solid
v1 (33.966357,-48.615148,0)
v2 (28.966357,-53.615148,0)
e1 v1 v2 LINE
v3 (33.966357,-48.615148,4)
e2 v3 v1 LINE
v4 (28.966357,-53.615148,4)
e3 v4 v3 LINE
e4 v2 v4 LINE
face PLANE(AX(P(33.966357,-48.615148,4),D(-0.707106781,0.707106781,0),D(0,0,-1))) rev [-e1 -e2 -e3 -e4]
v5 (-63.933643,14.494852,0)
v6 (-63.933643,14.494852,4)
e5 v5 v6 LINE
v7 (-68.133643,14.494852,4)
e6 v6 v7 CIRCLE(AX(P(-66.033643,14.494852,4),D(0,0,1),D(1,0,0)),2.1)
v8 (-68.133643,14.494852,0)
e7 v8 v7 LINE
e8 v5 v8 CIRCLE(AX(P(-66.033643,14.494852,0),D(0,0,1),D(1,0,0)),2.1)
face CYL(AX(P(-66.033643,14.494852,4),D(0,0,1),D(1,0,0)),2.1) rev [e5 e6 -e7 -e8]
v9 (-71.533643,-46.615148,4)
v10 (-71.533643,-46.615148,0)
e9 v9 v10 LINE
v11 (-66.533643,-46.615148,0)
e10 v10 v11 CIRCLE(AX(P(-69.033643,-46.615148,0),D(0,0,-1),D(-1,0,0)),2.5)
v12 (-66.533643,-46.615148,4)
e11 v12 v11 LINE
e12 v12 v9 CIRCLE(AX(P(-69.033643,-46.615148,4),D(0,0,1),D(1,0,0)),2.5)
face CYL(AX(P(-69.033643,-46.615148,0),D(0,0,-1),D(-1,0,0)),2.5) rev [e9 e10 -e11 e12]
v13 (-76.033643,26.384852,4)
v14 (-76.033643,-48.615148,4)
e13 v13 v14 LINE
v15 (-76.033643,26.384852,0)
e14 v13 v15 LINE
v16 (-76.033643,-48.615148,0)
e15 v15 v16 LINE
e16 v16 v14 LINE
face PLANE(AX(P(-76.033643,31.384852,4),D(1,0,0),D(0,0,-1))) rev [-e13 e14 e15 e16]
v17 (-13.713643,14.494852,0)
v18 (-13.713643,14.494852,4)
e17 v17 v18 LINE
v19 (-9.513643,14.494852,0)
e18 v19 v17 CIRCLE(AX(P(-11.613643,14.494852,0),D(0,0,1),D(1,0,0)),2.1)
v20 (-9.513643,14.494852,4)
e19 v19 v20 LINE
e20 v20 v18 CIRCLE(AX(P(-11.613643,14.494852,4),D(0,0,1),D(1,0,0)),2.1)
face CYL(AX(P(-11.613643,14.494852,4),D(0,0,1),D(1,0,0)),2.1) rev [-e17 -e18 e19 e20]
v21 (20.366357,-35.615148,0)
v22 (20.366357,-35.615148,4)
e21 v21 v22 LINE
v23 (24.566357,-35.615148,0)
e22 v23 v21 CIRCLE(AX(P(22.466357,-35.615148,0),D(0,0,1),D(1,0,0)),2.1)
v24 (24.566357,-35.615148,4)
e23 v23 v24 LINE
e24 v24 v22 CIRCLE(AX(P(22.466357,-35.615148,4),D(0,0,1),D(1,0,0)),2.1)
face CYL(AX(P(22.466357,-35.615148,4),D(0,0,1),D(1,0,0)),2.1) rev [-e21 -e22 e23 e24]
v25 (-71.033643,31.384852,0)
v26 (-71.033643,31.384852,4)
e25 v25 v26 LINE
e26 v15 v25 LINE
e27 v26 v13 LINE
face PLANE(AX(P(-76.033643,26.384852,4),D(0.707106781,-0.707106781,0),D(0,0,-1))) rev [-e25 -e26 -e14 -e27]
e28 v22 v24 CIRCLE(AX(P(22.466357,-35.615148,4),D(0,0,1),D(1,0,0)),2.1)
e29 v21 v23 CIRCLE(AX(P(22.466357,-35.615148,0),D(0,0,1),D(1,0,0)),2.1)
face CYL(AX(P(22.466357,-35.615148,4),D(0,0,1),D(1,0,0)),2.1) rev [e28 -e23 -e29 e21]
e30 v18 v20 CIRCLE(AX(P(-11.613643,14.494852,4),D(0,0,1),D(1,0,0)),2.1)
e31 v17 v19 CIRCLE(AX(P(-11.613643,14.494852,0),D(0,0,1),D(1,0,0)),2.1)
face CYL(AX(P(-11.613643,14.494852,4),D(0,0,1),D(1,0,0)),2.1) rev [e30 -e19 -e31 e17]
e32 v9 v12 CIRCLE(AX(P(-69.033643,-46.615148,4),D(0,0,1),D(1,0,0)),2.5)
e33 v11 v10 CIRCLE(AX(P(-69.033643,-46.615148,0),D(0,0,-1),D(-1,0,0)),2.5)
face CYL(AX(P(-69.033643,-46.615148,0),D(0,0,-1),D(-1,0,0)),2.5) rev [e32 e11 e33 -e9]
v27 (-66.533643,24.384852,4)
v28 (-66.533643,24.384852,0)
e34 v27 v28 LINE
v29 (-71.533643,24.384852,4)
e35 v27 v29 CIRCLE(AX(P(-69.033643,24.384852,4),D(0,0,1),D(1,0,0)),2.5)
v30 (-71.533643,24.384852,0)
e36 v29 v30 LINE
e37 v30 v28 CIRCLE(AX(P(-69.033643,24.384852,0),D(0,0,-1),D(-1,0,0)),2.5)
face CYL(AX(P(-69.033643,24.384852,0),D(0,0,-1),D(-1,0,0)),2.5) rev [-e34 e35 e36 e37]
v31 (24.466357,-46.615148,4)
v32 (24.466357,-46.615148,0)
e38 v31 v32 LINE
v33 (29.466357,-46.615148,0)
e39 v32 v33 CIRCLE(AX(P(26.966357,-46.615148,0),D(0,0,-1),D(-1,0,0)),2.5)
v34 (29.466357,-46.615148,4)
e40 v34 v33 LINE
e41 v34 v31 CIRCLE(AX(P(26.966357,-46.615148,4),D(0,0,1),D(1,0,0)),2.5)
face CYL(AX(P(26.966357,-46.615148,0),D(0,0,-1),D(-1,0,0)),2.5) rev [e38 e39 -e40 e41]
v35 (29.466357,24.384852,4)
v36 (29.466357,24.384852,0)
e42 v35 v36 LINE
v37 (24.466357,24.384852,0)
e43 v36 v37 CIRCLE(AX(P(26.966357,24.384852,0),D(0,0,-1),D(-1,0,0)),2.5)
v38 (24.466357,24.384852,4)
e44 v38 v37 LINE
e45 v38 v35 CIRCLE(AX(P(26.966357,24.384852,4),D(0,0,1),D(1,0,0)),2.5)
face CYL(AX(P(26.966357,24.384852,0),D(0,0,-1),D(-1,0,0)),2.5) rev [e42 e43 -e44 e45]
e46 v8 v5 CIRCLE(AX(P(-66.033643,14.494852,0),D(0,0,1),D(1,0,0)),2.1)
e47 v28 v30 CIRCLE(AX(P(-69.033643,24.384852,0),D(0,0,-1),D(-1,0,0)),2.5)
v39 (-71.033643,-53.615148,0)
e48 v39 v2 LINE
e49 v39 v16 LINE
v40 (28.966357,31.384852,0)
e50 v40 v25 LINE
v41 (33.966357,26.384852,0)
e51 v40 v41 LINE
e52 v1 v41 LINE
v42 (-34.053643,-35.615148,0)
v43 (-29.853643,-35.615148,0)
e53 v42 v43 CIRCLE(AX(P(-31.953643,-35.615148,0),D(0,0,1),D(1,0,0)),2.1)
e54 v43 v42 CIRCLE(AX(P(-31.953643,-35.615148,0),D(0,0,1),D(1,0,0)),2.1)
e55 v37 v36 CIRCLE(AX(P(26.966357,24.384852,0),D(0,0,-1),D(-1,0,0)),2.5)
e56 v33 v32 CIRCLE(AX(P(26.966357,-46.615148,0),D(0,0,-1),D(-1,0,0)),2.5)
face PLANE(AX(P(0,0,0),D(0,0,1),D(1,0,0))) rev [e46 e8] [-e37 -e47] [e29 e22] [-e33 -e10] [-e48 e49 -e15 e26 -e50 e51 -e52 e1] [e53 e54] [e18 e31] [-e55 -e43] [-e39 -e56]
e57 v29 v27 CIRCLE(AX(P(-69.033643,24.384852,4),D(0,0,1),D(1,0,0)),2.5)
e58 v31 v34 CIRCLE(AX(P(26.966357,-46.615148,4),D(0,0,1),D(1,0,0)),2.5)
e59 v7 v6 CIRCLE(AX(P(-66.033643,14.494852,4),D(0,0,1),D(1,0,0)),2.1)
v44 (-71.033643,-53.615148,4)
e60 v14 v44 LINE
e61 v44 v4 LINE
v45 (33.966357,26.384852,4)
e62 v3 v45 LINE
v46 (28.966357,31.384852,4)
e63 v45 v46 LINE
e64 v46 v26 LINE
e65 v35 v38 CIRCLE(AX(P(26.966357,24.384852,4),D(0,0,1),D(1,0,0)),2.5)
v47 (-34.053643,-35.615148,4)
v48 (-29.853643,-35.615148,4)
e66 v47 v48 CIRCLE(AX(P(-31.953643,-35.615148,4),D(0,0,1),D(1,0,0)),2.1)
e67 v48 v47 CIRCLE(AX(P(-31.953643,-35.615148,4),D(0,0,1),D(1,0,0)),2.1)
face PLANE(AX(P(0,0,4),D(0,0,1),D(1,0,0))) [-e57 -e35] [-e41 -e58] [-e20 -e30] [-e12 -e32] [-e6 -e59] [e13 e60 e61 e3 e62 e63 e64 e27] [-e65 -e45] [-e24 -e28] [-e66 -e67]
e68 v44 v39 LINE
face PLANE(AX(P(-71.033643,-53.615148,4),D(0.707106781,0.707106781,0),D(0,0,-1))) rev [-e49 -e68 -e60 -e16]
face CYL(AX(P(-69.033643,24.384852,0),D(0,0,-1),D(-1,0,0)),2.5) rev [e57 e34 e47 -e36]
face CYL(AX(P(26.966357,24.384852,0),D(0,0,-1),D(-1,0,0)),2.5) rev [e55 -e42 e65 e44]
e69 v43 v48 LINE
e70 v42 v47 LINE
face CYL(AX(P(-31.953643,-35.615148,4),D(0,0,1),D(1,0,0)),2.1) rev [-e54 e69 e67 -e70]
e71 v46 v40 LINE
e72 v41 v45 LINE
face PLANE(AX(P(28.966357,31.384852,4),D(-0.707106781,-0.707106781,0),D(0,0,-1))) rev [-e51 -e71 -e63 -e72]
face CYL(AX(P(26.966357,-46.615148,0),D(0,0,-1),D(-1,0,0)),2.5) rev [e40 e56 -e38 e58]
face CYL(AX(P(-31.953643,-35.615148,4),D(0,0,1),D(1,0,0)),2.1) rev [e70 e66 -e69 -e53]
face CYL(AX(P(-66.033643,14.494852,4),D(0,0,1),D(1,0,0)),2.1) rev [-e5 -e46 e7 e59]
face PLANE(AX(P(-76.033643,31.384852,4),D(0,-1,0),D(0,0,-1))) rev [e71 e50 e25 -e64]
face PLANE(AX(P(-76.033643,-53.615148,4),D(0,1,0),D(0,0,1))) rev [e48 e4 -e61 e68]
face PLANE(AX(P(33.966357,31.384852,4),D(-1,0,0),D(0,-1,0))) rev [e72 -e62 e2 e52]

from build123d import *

# Parameters (mm, degrees)
SKETCH_1_W                = 110
SKETCH_1_H                = 85
EXTRUDE_1_DEPTH           = 4
HOLE_WIZARD_M5_1_D        = 4.2
HOLE_WIZARD_M5_1_DEPTH    = 16
HOLE_WIZARD_M5_1_TIP      = 1.2618073
CHAMFER_1_SIZE            = 5
HOLE_WIZARD_5_0_5_1_D     = 5
HOLE_WIZARD_5_0_5_1_DEPTH = 10
HOLE_WIZARD_5_0_5_1_TIP   = 1.443375673


with BuildPart() as part:
    # 草图1 → 凸台-拉伸1 (new body)
    with BuildSketch(Plane.XY):
        with Locations((-21.033643231, -11.115148183)):
            Rectangle(SKETCH_1_W, SKETCH_1_H)
    extrude(amount=EXTRUDE_1_DEPTH)

    # M5 螺纹孔1
    with Locations(Plane.XY.offset(4)):
        with Locations((-66.033643231, 14.494851817), (-31.953643231, -35.615148183), (-11.613643231, 14.494851817), (22.466356769, -35.615148183)):
            Hole(HOLE_WIZARD_M5_1_D / 2, depth=HOLE_WIZARD_M5_1_DEPTH)
            with Locations((0, 0, -(HOLE_WIZARD_M5_1_DEPTH + HOLE_WIZARD_M5_1_TIP / 2))):  # 118° drill point
                Cone(0, HOLE_WIZARD_M5_1_D / 2, HOLE_WIZARD_M5_1_TIP, mode=Mode.SUBTRACT)

    # 倒角1
    chamfer_1_edges = [part.edges().sort_by_distance(p)[0] for p in [
        (-76.033643231, 31.384851817, 2),
        (33.966356769, 31.384851817, 2),
        (33.966356769, -53.615148183, 2),
        (-76.033643231, -53.615148183, 2),
    ]]
    chamfer(chamfer_1_edges, length=CHAMFER_1_SIZE)

    # Ø5.0 (5) 直径孔1
    with Locations(Plane(origin=(0, 0, 0), x_dir=(-1, 0, 0), z_dir=(0, 0, -1))):
        with Locations((69.033643231, 24.384851817), (69.033643231, -46.615148183), (-26.966356769, -46.615148183), (-26.966356769, 24.384851817)):
            Hole(HOLE_WIZARD_5_0_5_1_D / 2, depth=HOLE_WIZARD_5_0_5_1_DEPTH)
            with Locations((0, 0, -(HOLE_WIZARD_5_0_5_1_DEPTH + HOLE_WIZARD_5_0_5_1_TIP / 2))):  # 120° drill point
                Cone(0, HOLE_WIZARD_5_0_5_1_D / 2, HOLE_WIZARD_5_0_5_1_TIP, mode=Mode.SUBTRACT)


solid = part.part
